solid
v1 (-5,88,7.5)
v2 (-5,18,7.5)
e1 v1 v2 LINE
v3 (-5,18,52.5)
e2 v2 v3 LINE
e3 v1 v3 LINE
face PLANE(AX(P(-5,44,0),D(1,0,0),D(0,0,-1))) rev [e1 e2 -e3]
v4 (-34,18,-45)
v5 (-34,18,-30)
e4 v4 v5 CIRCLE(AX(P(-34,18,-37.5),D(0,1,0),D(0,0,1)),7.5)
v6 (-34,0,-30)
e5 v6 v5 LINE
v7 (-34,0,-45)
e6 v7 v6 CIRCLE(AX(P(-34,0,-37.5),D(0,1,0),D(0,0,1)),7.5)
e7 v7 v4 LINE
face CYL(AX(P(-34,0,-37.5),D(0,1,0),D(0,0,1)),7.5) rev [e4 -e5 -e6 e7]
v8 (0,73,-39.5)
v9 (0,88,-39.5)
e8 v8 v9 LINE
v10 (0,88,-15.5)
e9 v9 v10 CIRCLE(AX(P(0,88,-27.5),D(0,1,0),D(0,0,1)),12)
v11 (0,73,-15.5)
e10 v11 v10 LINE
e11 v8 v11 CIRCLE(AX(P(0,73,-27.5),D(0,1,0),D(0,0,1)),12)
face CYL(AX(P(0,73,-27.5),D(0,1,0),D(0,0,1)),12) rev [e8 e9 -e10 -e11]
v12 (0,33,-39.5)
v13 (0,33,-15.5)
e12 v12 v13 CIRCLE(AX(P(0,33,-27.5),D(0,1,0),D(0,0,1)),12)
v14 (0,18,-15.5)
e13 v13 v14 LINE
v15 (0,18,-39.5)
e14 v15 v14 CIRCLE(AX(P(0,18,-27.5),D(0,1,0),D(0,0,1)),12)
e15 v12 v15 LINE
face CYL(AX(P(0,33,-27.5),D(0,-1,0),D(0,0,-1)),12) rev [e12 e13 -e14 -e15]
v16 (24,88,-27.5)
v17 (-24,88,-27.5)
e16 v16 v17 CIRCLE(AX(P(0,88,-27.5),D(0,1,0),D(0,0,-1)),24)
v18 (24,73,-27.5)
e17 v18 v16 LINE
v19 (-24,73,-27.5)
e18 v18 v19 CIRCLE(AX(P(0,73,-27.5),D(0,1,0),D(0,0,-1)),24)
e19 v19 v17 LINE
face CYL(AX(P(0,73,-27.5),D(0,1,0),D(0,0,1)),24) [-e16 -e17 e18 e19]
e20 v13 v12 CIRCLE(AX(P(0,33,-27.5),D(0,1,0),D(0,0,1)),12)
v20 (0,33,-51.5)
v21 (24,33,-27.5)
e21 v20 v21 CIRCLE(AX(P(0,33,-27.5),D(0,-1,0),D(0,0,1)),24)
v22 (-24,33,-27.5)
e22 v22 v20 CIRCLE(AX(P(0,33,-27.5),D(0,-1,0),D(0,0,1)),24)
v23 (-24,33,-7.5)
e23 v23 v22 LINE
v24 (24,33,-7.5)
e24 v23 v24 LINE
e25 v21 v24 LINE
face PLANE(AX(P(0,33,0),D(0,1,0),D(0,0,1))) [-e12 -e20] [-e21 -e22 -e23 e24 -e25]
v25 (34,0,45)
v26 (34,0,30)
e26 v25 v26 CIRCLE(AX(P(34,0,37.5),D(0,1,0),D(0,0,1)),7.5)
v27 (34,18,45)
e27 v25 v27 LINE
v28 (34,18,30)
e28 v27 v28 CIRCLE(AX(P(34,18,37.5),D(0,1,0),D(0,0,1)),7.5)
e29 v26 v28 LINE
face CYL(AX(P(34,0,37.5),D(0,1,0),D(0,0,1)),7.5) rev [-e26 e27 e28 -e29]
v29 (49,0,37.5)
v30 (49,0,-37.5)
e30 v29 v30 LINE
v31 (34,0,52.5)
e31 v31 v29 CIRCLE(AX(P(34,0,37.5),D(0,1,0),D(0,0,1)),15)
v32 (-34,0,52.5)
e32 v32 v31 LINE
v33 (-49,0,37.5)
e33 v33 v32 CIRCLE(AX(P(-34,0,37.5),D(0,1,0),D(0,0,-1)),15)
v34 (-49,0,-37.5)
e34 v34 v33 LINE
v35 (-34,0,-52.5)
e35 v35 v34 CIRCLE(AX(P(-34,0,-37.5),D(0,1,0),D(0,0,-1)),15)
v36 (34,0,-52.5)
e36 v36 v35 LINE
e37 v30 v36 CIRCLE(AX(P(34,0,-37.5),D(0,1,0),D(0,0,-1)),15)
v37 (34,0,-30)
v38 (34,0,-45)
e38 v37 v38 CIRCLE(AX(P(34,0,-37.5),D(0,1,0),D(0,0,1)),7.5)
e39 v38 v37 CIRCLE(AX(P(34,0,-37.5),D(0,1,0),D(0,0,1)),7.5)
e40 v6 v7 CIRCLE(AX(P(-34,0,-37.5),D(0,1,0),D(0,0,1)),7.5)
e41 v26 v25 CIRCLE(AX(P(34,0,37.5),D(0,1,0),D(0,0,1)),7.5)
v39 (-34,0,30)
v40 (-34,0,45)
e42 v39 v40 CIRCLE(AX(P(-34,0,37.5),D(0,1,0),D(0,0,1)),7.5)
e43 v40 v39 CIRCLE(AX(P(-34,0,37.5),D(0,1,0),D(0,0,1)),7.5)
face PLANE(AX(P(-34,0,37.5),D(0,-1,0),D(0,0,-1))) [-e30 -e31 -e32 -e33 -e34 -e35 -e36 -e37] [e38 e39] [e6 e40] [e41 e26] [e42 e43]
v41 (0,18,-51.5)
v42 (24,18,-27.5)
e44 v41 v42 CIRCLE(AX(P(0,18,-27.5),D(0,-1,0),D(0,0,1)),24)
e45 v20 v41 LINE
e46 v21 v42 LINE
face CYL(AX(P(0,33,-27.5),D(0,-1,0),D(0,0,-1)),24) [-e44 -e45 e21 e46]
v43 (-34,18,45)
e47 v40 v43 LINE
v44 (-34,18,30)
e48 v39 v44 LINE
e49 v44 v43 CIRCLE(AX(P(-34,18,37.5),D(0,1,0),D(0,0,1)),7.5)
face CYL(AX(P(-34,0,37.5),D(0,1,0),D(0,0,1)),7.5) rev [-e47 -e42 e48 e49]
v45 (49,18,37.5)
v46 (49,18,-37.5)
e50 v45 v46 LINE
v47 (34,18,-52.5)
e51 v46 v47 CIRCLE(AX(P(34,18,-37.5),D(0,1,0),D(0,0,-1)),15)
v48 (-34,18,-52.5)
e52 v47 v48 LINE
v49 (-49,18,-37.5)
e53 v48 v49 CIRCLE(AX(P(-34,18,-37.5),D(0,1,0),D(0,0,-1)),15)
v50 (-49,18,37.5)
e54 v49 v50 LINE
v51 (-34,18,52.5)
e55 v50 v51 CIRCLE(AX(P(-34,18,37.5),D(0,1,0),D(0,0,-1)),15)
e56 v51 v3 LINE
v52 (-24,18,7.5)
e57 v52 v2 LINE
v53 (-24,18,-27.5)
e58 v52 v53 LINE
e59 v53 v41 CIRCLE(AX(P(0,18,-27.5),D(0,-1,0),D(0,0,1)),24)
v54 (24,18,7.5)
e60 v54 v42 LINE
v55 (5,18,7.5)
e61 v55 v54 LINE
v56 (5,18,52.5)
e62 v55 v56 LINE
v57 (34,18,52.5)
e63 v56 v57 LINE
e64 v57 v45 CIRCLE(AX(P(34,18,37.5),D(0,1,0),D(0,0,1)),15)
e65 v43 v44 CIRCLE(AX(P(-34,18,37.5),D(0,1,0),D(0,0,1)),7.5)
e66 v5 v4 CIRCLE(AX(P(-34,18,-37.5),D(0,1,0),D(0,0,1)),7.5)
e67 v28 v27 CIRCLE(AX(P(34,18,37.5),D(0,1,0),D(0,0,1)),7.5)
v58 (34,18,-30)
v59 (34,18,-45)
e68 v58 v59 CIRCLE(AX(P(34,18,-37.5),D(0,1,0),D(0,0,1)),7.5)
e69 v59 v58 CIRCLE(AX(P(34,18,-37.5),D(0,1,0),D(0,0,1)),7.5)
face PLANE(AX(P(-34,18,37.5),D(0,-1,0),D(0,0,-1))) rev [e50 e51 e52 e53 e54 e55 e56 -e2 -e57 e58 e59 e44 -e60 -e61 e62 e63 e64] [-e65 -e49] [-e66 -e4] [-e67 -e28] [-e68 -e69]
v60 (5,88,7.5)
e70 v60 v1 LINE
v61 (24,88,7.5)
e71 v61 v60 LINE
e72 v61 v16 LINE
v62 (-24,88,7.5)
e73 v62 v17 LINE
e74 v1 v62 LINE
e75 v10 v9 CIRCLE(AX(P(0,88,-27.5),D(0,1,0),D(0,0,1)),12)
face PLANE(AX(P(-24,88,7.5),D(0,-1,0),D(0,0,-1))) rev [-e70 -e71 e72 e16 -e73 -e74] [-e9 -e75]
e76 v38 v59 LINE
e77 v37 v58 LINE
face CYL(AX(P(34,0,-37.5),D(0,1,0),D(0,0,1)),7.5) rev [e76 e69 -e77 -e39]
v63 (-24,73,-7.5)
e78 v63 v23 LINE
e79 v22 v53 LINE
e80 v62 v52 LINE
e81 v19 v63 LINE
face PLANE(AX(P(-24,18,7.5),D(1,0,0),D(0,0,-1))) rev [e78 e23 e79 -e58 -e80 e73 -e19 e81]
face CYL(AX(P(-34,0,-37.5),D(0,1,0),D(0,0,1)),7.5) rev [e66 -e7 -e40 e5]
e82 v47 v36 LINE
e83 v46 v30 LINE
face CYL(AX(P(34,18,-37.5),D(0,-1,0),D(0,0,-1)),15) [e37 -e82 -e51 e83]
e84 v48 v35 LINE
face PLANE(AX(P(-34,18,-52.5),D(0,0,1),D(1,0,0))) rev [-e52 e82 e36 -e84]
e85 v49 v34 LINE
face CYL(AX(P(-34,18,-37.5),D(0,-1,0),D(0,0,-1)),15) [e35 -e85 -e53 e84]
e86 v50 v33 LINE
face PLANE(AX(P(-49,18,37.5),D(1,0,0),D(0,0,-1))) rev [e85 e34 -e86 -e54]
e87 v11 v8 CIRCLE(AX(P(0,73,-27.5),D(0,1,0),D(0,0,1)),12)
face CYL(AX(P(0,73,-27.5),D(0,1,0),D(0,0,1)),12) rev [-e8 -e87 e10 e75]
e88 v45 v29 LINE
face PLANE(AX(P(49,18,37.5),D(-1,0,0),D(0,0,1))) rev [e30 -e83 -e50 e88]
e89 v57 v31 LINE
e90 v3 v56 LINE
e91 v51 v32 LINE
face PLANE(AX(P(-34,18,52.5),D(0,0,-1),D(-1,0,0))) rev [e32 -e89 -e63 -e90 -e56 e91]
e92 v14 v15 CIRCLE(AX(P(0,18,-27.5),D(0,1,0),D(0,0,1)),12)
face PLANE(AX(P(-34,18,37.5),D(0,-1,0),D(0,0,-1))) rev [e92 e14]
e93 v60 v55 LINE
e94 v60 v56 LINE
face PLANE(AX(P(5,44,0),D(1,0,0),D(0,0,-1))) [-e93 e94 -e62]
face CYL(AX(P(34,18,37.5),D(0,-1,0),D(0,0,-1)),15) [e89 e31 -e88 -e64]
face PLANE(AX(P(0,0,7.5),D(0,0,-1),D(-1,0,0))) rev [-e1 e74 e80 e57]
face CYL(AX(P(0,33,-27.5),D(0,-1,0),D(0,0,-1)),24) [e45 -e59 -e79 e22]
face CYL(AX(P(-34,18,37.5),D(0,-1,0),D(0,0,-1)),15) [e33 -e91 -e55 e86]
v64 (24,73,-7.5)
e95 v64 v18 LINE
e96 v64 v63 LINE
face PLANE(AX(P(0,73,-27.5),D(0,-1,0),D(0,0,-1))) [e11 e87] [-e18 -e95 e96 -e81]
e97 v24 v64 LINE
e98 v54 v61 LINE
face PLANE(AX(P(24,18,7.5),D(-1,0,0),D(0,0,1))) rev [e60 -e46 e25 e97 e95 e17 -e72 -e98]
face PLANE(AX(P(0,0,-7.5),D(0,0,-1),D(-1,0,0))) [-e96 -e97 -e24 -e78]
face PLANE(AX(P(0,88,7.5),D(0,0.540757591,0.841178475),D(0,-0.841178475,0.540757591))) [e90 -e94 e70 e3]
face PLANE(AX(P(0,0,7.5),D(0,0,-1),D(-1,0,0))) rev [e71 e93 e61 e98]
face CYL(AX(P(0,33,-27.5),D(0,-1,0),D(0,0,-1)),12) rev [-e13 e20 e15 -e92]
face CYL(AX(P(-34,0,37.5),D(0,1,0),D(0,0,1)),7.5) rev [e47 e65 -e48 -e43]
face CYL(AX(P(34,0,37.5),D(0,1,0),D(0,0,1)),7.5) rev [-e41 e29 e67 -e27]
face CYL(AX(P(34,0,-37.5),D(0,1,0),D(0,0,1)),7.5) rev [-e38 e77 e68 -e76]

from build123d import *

# Parameters (mm, degrees)
BASE_PLATE_DEPTH           = 18
MOUNTING_HOLES_SKETCH_R    = 7.5
MOUNTING_HOLES_4X_15_DEPTH = 18
UPRIGHT_COLUMN_SKETCH_W    = 48
UPRIGHT_COLUMN_SKETCH_H    = 70
UPRIGHT_COLUMN_DEPTH       = 7.5
SUPPORT_RIB_REACH          = 115.584
SUPPORT_RIB_SKETCH_WALL_W  = 312.383924088
SUPPORT_RIB_SKETCH_WALL_H  = 10
CLEVIS_LUG_1_SKETCH_R      = 12
CLEVIS_LUG_1_DEPTH         = 15
CLEVIS_START               = 15
CLEVIS_LUG_2_SKETCH_R      = 12
CLEVIS_LUG_2_DEPTH         = 15


with BuildPart() as part:
    # Base Plate Sketch → Base Plate (new body)
    with BuildSketch(Plane(origin=(0, 0, 0), x_dir=(1, 0, 0), z_dir=(0, 1, 0))):
        with BuildLine():
            Line((-34, -52.5), (34, -52.5))
            ThreePointArc((34, -52.5), (44.606601718, -48.106601718), (49, -37.5))
            Line((49, -37.5), (49, 37.5))
            ThreePointArc((49, 37.5), (44.606601718, 48.106601718), (34, 52.5))
            Line((34, 52.5), (-34, 52.5))
            ThreePointArc((-34, 52.5), (-44.606601718, 48.106601718), (-49, 37.5))
            Line((-49, 37.5), (-49, -37.5))
            ThreePointArc((-49, -37.5), (-44.606601718, -48.106601718), (-34, -52.5))
        make_face()
    extrude(amount=BASE_PLATE_DEPTH)

    # Mounting Holes Sketch → Mounting Holes 4xØ15 (cut)
    with BuildSketch(Plane(origin=(0, 18, 0), x_dir=(1, 0, 0), z_dir=(0, 1, 0))):
        with Locations(Location((-34, 37.5, 0), (0, 0, 270))):
            Circle(MOUNTING_HOLES_SKETCH_R)
        with Locations(Location((34, 37.5, 0), (0, 0, 270))):
            Circle(MOUNTING_HOLES_SKETCH_R)
        with Locations(Location((-34, -37.5, 0), (0, 0, 270))):
            Circle(MOUNTING_HOLES_SKETCH_R)
        with Locations(Location((34, -37.5, 0), (0, 0, 270))):
            Circle(MOUNTING_HOLES_SKETCH_R)
    extrude(amount=-MOUNTING_HOLES_4X_15_DEPTH, mode=Mode.SUBTRACT)

    # Upright Column Sketch → Upright Column (add, symmetric)
    with BuildSketch(Plane.XY):
        with Locations((0, 53)):
            Rectangle(UPRIGHT_COLUMN_SKETCH_W, UPRIGHT_COLUMN_SKETCH_H)
    extrude(amount=UPRIGHT_COLUMN_DEPTH, both=True)

    # Support Rib Sketch wall → Support Rib (add, up to next)
    with BuildSketch(Plane(origin=(0, 53, 30), x_dir=(0, -0.841178475377, 0.540757591313), z_dir=(0, -0.540757591313, -0.841178475377)), mode=Mode.PRIVATE) as support_rib_sk1:
        Rectangle(SUPPORT_RIB_SKETCH_WALL_W, SUPPORT_RIB_SKETCH_WALL_H)
    support_rib_tool1 = extrude(support_rib_sk1.sketch, amount=SUPPORT_RIB_REACH, mode=Mode.PRIVATE) - part.part
    add(support_rib_tool1.solids().sort_by_distance((0, 53, 30))[0])

    # Clevis Lug 1 Sketch → Clevis Lug 1 (add)
    with BuildSketch(Plane(origin=(0, 88, 0), x_dir=(1, 0, 0), z_dir=(0, 1, 0))):
        with BuildLine():
            Line((-24, -7.5), (-24, 27.5))
            ThreePointArc((-24, 27.5), (0, 51.5), (24, 27.5))
            Line((24, 27.5), (24, -7.5))
            Line((24, -7.5), (-24, -7.5))
        make_face()
        with Locations(Location((0, 27.5, 0), (0, 0, 270))):
            Circle(CLEVIS_LUG_1_SKETCH_R, mode=Mode.SUBTRACT)
    extrude(amount=-CLEVIS_LUG_1_DEPTH)

    # Clevis Lug 2 Sketch → Clevis Lug 2 (add)
    with BuildSketch(Plane(origin=(0, 18, 0), x_dir=(1, 0, 0), z_dir=(0, 1, 0)).offset(CLEVIS_START)):
        with BuildLine():
            Line((-24, 27.5), (-24, 7.5))
            Line((-24, 7.5), (24, 7.5))
            Line((24, 7.5), (24, 27.5))
            ThreePointArc((24, 27.5), (0, 51.5), (-24, 27.5))
        make_face()
        with Locations(Location((0, 27.5, 0), (0, 0, 270))):
            Circle(CLEVIS_LUG_2_SKETCH_R, mode=Mode.SUBTRACT)
    extrude(amount=-CLEVIS_LUG_2_DEPTH)


solid = part.part
